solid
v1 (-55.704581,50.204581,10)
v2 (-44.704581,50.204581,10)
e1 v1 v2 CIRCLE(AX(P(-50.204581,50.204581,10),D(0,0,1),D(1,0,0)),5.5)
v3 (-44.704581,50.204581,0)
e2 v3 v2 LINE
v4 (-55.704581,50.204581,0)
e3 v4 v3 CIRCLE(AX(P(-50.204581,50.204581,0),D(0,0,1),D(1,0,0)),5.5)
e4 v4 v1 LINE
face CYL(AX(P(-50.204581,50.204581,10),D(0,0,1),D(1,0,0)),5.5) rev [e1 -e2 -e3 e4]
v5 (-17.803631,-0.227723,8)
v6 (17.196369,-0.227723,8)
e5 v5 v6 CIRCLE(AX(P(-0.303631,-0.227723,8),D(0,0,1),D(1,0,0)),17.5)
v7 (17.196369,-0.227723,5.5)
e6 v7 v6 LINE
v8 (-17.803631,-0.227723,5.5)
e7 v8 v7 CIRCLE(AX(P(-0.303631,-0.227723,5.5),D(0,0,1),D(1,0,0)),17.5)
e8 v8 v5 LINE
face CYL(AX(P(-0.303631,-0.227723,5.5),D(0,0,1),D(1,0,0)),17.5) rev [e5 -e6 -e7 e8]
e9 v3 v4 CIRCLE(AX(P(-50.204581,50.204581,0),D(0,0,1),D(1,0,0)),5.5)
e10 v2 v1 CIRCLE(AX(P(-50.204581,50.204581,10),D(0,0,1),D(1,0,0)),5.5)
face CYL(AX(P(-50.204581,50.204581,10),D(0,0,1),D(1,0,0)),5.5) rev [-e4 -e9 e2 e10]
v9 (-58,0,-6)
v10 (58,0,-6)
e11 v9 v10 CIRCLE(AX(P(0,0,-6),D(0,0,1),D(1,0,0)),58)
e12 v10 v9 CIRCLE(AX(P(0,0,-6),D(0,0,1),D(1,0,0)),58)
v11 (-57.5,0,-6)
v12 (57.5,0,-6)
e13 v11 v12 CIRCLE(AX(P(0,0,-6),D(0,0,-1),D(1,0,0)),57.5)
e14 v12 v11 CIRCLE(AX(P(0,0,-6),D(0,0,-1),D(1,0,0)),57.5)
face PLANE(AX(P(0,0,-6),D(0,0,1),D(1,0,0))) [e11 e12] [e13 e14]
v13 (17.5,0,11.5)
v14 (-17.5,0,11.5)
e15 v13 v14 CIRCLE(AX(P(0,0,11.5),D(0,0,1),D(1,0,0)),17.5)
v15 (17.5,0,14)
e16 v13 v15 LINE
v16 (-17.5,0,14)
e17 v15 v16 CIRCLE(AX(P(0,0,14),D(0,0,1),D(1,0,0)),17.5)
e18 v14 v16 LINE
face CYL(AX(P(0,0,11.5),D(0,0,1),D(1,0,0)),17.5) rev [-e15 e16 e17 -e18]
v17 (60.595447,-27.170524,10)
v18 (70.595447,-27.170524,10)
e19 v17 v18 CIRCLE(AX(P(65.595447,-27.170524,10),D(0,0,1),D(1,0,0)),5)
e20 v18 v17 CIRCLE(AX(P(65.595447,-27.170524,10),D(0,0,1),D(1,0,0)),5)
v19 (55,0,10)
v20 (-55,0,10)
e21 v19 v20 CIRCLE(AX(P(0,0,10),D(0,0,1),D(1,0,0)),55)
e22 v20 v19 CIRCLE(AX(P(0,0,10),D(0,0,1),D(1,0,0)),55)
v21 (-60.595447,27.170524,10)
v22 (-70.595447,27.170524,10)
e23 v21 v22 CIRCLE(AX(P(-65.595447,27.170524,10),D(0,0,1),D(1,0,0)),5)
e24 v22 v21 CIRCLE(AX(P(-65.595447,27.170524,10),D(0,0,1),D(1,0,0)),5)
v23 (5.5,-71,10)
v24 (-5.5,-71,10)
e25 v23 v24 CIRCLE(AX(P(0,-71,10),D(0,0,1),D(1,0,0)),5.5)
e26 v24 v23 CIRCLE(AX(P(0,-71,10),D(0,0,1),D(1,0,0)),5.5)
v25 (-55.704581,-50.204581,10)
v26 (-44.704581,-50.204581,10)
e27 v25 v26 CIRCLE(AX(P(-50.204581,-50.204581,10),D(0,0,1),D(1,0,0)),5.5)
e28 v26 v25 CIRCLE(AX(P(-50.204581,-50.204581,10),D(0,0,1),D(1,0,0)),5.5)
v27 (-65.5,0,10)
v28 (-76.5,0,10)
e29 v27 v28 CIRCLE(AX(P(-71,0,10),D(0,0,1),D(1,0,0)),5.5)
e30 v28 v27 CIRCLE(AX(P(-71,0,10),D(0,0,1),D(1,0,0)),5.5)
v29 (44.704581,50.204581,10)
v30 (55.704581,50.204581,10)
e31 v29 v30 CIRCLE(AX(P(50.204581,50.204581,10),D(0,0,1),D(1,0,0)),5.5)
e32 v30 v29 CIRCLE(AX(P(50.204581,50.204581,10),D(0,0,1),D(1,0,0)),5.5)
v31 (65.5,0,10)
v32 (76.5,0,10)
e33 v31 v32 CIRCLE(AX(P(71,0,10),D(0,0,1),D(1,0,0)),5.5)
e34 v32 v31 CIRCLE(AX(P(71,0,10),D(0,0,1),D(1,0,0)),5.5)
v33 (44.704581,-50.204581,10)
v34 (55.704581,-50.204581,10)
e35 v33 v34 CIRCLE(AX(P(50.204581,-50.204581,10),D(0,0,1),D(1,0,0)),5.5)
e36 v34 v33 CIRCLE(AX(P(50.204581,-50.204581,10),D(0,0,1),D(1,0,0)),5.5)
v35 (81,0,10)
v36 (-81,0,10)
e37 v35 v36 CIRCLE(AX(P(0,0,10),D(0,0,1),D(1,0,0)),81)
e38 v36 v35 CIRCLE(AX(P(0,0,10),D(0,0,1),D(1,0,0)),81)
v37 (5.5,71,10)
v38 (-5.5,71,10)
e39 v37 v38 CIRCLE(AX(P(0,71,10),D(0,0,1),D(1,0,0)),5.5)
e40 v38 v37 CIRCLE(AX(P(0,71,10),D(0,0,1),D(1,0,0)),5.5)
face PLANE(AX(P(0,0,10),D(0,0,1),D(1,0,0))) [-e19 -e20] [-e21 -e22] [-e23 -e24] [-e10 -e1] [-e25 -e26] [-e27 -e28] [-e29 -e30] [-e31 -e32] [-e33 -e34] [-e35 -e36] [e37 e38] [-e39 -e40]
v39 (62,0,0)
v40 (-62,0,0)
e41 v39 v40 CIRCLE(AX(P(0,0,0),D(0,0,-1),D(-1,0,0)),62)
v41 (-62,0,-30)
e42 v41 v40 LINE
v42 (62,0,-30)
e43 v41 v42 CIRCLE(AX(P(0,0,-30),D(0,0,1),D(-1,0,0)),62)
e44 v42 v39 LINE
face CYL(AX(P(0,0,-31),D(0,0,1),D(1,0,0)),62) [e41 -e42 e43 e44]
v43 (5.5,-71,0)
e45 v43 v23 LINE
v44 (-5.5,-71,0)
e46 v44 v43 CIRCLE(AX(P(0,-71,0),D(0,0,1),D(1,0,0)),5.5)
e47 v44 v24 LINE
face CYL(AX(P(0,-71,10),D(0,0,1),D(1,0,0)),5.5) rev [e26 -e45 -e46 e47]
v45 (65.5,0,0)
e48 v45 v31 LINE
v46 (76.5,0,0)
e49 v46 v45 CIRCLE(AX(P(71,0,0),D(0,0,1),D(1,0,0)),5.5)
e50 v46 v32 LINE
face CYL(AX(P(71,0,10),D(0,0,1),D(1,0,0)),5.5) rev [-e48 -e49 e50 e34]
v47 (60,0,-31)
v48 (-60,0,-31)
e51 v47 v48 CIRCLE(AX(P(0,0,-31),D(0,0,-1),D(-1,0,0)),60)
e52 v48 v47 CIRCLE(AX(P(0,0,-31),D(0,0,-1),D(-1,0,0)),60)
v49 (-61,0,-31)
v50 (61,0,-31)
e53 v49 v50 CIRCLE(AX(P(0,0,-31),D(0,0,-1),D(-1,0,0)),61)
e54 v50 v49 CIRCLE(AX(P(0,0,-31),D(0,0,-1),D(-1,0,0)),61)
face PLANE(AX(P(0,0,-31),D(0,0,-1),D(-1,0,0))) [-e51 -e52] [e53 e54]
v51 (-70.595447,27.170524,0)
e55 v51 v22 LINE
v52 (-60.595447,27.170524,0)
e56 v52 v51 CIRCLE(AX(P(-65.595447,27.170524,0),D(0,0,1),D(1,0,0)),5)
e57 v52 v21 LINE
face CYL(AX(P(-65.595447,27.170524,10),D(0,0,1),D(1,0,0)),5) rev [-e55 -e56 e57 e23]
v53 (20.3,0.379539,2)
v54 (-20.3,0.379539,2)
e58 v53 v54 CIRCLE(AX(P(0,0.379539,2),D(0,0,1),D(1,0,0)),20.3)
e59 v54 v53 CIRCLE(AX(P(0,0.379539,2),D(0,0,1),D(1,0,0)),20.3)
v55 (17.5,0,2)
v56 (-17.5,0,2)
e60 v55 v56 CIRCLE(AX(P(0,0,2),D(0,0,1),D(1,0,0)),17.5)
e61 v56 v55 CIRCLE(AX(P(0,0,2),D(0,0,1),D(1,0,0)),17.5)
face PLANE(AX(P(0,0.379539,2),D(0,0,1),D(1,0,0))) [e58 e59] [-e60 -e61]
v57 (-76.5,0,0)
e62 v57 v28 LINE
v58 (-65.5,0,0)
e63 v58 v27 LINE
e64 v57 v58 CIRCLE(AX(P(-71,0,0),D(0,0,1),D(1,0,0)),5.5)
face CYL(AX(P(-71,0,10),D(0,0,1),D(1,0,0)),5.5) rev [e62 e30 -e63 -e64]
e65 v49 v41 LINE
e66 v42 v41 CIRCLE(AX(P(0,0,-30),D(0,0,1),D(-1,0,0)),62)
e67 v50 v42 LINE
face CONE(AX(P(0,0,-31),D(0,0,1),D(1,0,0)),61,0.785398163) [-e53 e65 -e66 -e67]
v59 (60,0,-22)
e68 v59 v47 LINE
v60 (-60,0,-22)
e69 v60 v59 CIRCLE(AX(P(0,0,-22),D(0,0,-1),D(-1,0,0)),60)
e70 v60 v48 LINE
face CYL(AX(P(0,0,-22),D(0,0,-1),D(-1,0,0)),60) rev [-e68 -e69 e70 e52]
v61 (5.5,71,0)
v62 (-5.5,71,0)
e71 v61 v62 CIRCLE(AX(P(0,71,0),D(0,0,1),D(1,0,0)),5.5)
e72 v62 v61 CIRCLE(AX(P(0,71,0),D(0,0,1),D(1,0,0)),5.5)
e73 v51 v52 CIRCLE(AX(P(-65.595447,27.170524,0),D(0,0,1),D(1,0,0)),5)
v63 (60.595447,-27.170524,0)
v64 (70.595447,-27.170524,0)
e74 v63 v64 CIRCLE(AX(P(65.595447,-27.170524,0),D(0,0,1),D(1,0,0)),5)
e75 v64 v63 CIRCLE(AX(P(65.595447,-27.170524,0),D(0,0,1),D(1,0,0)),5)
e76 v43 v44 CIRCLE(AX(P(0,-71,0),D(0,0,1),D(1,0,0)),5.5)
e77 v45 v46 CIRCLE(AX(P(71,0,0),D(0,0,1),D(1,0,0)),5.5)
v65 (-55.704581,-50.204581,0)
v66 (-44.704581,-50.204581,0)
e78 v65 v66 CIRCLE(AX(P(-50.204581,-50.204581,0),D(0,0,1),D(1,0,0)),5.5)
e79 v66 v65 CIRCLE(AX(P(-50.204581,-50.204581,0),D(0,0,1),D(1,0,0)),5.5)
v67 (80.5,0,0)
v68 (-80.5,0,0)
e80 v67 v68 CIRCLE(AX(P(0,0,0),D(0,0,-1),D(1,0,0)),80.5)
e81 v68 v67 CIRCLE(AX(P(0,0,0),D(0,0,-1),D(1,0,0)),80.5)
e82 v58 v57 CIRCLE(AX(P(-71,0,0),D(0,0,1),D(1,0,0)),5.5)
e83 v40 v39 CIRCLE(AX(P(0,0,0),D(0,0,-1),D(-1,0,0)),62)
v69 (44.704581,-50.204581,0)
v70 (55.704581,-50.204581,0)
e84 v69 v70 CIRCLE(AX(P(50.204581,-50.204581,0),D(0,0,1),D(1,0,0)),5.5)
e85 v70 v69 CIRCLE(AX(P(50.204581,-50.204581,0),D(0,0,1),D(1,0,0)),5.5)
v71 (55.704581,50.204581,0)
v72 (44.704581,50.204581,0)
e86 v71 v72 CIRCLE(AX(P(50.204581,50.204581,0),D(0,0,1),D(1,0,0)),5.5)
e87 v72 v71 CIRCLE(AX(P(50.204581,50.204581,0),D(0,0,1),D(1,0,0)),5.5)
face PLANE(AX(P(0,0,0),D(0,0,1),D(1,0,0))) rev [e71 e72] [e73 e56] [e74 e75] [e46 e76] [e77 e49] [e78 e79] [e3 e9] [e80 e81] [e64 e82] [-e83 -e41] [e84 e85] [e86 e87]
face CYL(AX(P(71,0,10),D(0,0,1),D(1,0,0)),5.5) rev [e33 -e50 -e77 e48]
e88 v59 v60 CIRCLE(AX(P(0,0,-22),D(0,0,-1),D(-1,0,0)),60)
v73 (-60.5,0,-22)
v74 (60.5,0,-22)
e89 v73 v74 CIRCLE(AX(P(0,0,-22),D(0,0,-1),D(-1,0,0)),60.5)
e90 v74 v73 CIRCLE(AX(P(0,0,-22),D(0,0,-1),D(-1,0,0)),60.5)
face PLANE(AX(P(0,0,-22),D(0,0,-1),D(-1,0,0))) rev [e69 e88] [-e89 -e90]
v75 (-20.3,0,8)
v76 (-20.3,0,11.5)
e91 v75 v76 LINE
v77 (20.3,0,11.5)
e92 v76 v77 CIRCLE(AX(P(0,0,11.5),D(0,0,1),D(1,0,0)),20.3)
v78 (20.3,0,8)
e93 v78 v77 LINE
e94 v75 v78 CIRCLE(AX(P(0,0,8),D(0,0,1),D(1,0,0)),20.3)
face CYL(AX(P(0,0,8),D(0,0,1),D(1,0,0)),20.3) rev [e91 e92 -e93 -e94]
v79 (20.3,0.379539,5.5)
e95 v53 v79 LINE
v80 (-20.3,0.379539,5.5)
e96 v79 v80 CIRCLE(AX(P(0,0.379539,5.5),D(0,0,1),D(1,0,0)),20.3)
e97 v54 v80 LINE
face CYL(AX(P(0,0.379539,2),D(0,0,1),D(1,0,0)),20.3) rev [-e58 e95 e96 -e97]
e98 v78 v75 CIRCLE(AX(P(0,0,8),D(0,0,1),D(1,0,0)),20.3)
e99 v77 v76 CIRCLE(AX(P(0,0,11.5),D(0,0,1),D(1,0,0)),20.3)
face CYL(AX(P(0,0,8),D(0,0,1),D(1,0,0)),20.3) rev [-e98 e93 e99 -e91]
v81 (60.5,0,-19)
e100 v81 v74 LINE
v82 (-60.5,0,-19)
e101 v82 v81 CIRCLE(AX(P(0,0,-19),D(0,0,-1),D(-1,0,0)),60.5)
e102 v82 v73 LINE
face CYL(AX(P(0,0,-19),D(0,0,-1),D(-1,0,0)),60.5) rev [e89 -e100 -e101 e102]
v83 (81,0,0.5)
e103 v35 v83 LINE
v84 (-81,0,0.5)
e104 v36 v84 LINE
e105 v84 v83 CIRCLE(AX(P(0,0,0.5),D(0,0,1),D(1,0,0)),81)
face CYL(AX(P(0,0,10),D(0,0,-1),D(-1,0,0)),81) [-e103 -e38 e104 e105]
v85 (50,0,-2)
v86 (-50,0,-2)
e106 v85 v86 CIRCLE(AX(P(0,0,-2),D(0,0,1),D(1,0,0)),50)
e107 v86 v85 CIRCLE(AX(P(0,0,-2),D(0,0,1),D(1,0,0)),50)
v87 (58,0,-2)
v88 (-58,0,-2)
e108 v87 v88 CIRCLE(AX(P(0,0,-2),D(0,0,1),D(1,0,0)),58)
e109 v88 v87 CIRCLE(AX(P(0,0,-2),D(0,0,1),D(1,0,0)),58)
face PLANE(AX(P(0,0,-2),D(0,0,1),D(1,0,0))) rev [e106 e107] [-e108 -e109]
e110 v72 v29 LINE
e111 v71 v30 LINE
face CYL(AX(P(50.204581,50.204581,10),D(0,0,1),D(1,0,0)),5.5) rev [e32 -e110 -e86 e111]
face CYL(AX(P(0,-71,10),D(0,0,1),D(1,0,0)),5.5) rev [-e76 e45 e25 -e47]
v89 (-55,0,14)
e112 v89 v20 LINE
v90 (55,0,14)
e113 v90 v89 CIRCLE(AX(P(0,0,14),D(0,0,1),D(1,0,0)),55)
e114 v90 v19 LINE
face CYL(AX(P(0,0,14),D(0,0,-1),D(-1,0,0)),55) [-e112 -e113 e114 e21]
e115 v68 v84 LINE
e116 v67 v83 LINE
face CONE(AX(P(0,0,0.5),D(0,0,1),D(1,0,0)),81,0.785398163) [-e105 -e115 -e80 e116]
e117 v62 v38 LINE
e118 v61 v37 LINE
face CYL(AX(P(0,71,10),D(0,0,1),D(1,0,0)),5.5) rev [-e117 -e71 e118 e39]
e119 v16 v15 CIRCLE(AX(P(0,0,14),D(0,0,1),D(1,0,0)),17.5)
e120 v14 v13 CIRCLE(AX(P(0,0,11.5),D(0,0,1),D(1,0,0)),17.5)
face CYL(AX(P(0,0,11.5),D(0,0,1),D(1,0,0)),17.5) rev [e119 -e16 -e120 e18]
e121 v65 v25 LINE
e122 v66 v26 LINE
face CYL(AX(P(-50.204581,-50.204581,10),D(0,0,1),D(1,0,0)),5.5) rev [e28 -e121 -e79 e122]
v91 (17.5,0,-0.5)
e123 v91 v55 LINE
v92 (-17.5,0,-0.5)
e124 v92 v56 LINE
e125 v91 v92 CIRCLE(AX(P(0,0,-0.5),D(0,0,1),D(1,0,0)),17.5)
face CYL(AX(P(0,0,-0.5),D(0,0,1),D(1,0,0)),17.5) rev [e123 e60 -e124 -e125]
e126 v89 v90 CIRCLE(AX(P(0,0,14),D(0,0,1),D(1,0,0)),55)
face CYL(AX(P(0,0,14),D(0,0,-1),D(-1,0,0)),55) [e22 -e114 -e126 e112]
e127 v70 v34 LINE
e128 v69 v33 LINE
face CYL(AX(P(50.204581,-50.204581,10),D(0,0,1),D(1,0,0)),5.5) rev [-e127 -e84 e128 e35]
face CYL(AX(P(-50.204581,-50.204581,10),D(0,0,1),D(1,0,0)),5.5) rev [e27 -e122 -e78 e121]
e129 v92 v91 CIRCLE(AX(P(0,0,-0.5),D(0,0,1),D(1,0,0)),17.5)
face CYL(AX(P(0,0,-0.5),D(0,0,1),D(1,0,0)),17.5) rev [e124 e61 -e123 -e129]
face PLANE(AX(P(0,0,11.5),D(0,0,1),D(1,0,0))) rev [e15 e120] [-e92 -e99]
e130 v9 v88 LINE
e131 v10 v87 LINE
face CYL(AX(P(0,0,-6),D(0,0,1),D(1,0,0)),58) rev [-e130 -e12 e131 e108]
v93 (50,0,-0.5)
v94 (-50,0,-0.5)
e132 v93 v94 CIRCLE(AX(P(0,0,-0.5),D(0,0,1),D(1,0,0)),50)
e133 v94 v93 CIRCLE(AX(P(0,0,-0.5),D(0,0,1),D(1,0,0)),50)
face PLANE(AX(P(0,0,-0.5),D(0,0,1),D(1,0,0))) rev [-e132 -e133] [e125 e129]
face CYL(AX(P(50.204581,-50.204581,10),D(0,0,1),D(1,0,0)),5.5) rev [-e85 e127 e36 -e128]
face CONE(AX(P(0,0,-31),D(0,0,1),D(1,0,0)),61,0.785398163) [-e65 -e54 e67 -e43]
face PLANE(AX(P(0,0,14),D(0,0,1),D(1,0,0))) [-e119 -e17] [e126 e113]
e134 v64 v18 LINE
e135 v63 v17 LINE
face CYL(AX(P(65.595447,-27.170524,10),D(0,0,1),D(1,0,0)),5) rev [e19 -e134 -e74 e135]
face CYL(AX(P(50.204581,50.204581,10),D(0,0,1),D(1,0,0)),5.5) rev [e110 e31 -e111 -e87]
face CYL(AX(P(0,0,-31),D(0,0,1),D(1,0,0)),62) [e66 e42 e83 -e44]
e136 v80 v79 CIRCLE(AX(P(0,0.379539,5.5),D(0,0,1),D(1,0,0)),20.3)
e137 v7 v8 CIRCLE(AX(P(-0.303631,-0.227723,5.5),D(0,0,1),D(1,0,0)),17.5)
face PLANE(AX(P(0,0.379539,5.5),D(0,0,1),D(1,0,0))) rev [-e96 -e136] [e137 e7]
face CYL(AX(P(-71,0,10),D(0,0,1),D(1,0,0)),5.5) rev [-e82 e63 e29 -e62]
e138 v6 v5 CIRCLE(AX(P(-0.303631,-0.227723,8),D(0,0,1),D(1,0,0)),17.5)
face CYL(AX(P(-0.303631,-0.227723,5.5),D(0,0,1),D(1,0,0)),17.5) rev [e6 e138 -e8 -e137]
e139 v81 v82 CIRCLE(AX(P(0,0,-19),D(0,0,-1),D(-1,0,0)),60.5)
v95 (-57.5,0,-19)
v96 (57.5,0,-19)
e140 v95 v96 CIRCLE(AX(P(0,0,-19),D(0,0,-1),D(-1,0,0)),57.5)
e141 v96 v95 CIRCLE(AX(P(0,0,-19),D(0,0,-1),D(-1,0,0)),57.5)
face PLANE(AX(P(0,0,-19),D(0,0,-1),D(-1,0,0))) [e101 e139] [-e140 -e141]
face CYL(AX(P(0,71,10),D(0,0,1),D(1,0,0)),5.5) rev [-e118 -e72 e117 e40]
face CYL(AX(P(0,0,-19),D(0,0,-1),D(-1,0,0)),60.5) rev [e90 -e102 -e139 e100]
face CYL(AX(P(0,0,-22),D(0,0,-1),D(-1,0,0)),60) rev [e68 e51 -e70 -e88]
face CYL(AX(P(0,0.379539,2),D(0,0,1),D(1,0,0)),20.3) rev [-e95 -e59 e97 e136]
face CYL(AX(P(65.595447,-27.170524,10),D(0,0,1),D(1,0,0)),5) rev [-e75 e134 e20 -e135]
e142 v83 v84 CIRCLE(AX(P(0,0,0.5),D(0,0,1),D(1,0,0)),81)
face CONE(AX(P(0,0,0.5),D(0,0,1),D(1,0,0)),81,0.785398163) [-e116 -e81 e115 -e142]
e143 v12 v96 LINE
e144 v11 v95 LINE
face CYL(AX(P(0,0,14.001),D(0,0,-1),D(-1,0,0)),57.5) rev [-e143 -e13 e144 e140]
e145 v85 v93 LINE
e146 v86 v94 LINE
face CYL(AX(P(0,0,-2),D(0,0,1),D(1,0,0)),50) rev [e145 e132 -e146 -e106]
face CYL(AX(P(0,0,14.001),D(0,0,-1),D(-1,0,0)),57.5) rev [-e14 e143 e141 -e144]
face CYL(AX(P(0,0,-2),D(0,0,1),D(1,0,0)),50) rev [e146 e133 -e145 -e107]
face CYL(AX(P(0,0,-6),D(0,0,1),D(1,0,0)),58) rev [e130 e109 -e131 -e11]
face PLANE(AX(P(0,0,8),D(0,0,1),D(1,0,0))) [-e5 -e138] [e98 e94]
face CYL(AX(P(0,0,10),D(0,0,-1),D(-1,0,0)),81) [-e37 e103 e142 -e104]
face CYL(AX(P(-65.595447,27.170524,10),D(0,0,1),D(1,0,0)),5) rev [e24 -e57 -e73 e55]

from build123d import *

# Parameters (mm, degrees)
SKETCH1_R                    = 81
BOSS_EXTRUDE1_DEPTH          = 10
SKETCH2_R                    = 55
BOSS_EXTRUDE2_DEPTH          = 4
SKETCH3_R                    = 62
BOSS_EXTRUDE3_DEPTH          = 31
SKETCH4_R                    = 17.5
CUT_EXTRUDE1_DEPTH           = 2.5
SKETCH5_R                    = 20.3
CUT_EXTRUDE2_DEPTH           = 3.5
SKETCH6_R                    = 17.5
CUT_EXTRUDE3_DEPTH           = 2.5
SKETCH7_R                    = 20.3
CUT_EXTRUDE4_DEPTH           = 3.5
SKETCH8_R                    = 17.5
CUT_EXTRUDE5_DEPTH           = 2.5
SKETCH9_R                    = 50
CUT_EXTRUDE6_DEPTH           = 1.5
F_1_0MM_BLIND_DOWEL_HOLE1_D  = 11
CIRPATTERN1_COUNT            = 8
F_10_0MM_BLIND_DOWEL_HOLE1_D = 10
SKETCH18_R                   = 58
CUT_EXTRUDE7_DEPTH           = 4
SKETCH19_R                   = 60
CUT_EXTRUDE8_DEPTH           = 9
SKETCH20_R                   = 60.5
CUT_EXTRUDE9_DEPTH           = 3
CUT_EXTRUDE10_REACH          = 121.21
SKETCH21_R                   = 57.5
CHAMFER1_SIZE                = 1
CHAMFER2_SIZE                = 0.5


with BuildPart() as part:
    # Sketch1 → Boss-Extrude1 (new body)
    with BuildSketch(Plane.XY):
        Circle(SKETCH1_R)
    extrude(amount=BOSS_EXTRUDE1_DEPTH)

    # Sketch2 → Boss-Extrude2 (add)
    with BuildSketch(Plane.XY.offset(10)):
        Circle(SKETCH2_R)
    extrude(amount=BOSS_EXTRUDE2_DEPTH)

    # Sketch3 → Boss-Extrude3 (add)
    with BuildSketch(Plane(origin=(0, 0, 0), x_dir=(-1, 0, 0), z_dir=(0, 0, -1))):
        Circle(SKETCH3_R)
    extrude(amount=BOSS_EXTRUDE3_DEPTH)

    # Sketch4 → Cut-Extrude1 (cut)
    with BuildSketch(Plane.XY.offset(14)):
        Circle(SKETCH4_R)
    extrude(amount=-CUT_EXTRUDE1_DEPTH, mode=Mode.SUBTRACT)

    # Sketch5 → Cut-Extrude2 (cut)
    with BuildSketch(Plane.XY.offset(11.5)):
        Circle(SKETCH5_R)
    extrude(amount=-CUT_EXTRUDE2_DEPTH, mode=Mode.SUBTRACT)

    # Sketch6 → Cut-Extrude3 (cut)
    with BuildSketch(Plane.XY.offset(8)):
        with Locations((-0.303631116, -0.227723337)):
            Circle(SKETCH6_R)
    extrude(amount=-CUT_EXTRUDE3_DEPTH, mode=Mode.SUBTRACT)

    # Sketch7 → Cut-Extrude4 (cut)
    with BuildSketch(Plane.XY.offset(5.5)):
        with Locations((0, 0.379538895)):
            Circle(SKETCH7_R)
    extrude(amount=-CUT_EXTRUDE4_DEPTH, mode=Mode.SUBTRACT)

    # Sketch8 → Cut-Extrude5 (cut)
    with BuildSketch(Plane.XY.offset(2)):
        Circle(SKETCH8_R)
    extrude(amount=-CUT_EXTRUDE5_DEPTH, mode=Mode.SUBTRACT)

    # Sketch9 → Cut-Extrude6 (cut)
    with BuildSketch(Plane.XY.offset(-0.5)):
        Circle(SKETCH9_R)
    extrude(amount=-CUT_EXTRUDE6_DEPTH, mode=Mode.SUBTRACT)

    # Ø1.0mm Blind Dowel Hole1 (through all)
    with Locations(Plane.XY.offset(10)):
        with Locations((0, 71)):
            f_1_0mm_blind_dowel_hole1 = Hole(F_1_0MM_BLIND_DOWEL_HOLE1_D / 2)

    # CirPattern1: Ø1.0mm Blind Dowel Hole1 ×8 about axis
    cirpattern1_axis = Axis((0, 0, 0), (0, 0, 1))
    for i in range(1, CIRPATTERN1_COUNT):
        add(f_1_0mm_blind_dowel_hole1.rotate(cirpattern1_axis, i * 360 / CIRPATTERN1_COUNT), mode=Mode.SUBTRACT)

    # Ø10.0mm Blind Dowel Hole1 (through all)
    with Locations(Plane.XY.offset(10)):
        with Locations((65.595446808, -27.170523698), (-65.595446808, 27.170523698)):
            Hole(F_10_0MM_BLIND_DOWEL_HOLE1_D / 2)

    # Sketch18 → Cut-Extrude7 (cut)
    with BuildSketch(Plane.XY.offset(-2)):
        Circle(SKETCH18_R)
    extrude(amount=-CUT_EXTRUDE7_DEPTH, mode=Mode.SUBTRACT)

    # Sketch19 → Cut-Extrude8 (cut)
    with BuildSketch(Plane(origin=(0, 0, -31), x_dir=(-1, 0, 0), z_dir=(0, 0, -1))):
        Circle(SKETCH19_R)
    extrude(amount=-CUT_EXTRUDE8_DEPTH, mode=Mode.SUBTRACT)

    # Sketch20 → Cut-Extrude9 (cut)
    with BuildSketch(Plane(origin=(0, 0, -22), x_dir=(-1, 0, 0), z_dir=(0, 0, -1))):
        Circle(SKETCH20_R)
    extrude(amount=-CUT_EXTRUDE9_DEPTH, mode=Mode.SUBTRACT)

    # Sketch21 → Cut-Extrude10 (cut, up to next)
    with BuildSketch(Plane(origin=(0, 0, -19), x_dir=(-1, 0, 0), z_dir=(0, 0, -1)), mode=Mode.PRIVATE) as cut_extrude10_sk1:
        Circle(SKETCH21_R)
    cut_extrude10_tool1 = extrude(cut_extrude10_sk1.sketch, amount=-CUT_EXTRUDE10_REACH, mode=Mode.PRIVATE) & part.part
    add(cut_extrude10_tool1.solids().sort_by_distance((0, 0, -19))[0], mode=Mode.SUBTRACT)

    # Chamfer1
    chamfer1_edges = [part.edges().sort_by_distance(p)[0] for p in [
        (62, 0, -31),
    ]]
    chamfer(chamfer1_edges, length=CHAMFER1_SIZE)

    # Chamfer2
    chamfer2_edges = [part.edges().sort_by_distance(p)[0] for p in [
        (-81, 0, 0),
    ]]
    chamfer(chamfer2_edges, length=CHAMFER2_SIZE)


solid = part.part
